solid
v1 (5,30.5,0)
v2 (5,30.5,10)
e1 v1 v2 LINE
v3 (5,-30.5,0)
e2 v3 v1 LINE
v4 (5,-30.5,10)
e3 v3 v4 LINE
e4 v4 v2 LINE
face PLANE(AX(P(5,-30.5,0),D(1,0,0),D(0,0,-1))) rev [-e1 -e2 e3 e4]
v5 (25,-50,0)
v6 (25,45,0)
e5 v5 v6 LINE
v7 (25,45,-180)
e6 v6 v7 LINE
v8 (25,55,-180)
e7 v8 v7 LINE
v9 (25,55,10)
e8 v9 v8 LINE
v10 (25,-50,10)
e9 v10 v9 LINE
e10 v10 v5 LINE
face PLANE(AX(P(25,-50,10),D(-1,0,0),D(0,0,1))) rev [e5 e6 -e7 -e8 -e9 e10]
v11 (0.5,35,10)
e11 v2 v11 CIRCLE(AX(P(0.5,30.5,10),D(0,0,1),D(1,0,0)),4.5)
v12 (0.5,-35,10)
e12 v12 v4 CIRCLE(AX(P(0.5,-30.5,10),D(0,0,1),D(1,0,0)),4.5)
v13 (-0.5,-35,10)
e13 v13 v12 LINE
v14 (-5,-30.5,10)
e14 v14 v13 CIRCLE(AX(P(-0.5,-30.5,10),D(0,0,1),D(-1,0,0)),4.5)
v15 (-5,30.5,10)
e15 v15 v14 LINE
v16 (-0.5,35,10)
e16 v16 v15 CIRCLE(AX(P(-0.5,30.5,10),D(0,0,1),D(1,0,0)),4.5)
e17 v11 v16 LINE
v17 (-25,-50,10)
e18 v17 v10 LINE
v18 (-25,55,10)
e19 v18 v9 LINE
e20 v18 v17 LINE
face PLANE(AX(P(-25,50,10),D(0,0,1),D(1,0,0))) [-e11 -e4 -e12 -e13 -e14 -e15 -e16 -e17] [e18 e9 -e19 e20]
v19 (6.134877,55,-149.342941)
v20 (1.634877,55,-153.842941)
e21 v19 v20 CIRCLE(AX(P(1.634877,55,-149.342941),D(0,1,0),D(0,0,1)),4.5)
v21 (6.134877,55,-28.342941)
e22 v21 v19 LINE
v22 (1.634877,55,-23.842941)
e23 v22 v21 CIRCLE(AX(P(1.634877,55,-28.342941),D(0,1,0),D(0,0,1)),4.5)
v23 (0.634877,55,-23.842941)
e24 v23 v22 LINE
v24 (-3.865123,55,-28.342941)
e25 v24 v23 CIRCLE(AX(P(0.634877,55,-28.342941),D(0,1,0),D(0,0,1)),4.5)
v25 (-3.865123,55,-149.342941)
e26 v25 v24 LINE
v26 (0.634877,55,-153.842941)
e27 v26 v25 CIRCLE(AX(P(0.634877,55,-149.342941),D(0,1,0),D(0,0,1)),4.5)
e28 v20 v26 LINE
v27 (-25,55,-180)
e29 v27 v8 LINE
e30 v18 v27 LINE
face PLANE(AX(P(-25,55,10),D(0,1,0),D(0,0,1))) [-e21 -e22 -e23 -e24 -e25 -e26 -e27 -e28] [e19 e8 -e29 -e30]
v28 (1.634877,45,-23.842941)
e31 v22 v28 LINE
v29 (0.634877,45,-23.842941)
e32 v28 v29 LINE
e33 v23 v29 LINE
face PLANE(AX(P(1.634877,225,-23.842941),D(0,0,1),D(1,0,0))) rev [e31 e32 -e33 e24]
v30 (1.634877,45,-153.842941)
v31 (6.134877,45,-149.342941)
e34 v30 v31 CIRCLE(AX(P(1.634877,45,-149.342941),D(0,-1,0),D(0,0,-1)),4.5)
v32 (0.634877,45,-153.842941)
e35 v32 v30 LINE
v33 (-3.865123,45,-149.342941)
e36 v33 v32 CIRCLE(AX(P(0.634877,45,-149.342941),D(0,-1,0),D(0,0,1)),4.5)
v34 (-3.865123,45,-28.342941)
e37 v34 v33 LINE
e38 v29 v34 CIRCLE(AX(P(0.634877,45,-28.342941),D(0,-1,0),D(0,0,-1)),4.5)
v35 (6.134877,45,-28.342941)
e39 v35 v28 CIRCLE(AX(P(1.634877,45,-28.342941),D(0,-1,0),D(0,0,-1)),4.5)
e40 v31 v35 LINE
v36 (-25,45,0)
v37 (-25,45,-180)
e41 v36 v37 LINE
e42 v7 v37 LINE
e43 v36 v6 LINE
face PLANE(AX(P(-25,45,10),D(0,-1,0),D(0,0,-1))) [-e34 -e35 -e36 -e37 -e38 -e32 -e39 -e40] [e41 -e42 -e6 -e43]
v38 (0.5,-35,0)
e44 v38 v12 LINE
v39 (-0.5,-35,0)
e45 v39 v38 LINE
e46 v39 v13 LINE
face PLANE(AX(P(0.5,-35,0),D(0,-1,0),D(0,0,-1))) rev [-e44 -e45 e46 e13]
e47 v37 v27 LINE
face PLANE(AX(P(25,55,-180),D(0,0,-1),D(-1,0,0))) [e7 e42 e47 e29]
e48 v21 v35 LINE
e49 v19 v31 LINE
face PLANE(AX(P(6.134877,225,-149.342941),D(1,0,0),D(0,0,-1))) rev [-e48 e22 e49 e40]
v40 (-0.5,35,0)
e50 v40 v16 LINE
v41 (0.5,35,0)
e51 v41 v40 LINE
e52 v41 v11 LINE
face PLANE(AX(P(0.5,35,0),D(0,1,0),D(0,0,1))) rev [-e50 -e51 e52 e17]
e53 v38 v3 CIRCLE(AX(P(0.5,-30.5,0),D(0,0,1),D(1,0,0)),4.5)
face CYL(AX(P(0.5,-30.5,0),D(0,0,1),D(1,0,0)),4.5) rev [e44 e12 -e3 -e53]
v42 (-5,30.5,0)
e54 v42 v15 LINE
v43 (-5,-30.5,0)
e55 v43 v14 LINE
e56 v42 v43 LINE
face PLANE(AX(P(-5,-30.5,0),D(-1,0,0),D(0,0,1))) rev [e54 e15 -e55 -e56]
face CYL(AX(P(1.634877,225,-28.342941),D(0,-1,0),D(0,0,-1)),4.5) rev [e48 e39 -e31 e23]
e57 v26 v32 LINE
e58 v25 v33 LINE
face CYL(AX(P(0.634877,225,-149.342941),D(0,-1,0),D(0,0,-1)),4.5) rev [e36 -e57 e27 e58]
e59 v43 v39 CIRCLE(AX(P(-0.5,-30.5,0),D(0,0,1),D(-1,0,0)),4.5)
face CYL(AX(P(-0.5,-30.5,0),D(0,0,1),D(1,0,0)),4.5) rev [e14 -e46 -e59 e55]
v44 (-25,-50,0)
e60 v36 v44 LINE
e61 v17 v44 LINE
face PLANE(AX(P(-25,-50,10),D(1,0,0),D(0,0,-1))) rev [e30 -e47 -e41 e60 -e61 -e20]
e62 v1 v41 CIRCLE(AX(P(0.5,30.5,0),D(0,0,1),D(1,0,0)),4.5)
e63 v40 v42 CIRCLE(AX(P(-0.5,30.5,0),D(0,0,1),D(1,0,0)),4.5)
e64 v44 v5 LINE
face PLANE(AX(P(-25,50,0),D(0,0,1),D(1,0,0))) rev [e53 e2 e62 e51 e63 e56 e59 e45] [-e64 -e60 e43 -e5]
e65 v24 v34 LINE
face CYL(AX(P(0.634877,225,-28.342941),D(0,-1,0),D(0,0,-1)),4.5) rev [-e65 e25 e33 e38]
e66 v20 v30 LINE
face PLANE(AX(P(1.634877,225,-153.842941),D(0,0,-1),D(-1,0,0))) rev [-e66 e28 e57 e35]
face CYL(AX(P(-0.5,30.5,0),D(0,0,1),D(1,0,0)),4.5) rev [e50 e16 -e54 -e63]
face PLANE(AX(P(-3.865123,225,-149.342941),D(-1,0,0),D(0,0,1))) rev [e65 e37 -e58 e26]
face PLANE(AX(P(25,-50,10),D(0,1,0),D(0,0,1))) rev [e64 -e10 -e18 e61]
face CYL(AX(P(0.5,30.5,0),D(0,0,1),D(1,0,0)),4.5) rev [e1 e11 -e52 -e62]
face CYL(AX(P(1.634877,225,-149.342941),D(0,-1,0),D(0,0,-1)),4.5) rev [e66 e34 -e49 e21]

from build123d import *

# Parameters (mm, degrees)
SKETCH1_W                = 50
SKETCH1_H                = 100
BOSS_EXTRUDE1_DEPTH      = 10
CUT_EXTRUDE1_DEPTH       = 10
BOSS_EXTRUDE2_DEPTH      = 180
BOSS_EXTRUDE2_DEPTH_BACK = 10
SKETCH3_W                = 50
SKETCH3_H                = 10
CUT_EXTRUDE2_DEPTH       = 180


with BuildPart() as part:
    # Sketch1 → Boss-Extrude1 (new body)
    with BuildSketch(Plane.XY):
        Rectangle(SKETCH1_W, SKETCH1_H)
    extrude(amount=BOSS_EXTRUDE1_DEPTH)

    # Sketch2 → Cut-Extrude1 (cut)
    with BuildSketch(Plane.XY.offset(10)):
        with BuildLine():
            Line((0.5, -35), (-0.5, -35))
            ThreePointArc((-0.5, -35), (-3.681980515, -33.681980515), (-5, -30.5))
            Line((-5, -30.5), (-5, 30.5))
            ThreePointArc((-5, 30.5), (-3.681980515, 33.681980515), (-0.5, 35))
            Line((-0.5, 35), (0.5, 35))
            ThreePointArc((0.5, 35), (3.681980515, 33.681980515), (5, 30.5))
            Line((5, 30.5), (5, -30.5))
            ThreePointArc((5, -30.5), (3.681980515, -33.681980515), (0.5, -35))
        make_face()
    extrude(amount=-CUT_EXTRUDE1_DEPTH, mode=Mode.SUBTRACT)

    # Sketch3 → Boss-Extrude2 (add, two sides: drawn at the far end of the back side and taken through both)
    with BuildSketch(Plane(origin=(0, 0, 0), x_dir=(-1, 0, 0), z_dir=(0, 0, -1)).offset(-BOSS_EXTRUDE2_DEPTH_BACK)):
        with Locations((0, 50)):
            Rectangle(SKETCH3_W, SKETCH3_H)
    extrude(amount=BOSS_EXTRUDE2_DEPTH + BOSS_EXTRUDE2_DEPTH_BACK)

    # Sketch4 → Cut-Extrude2 (cut)
    with BuildSketch(Plane.XZ.offset(-45)):
        with BuildLine():
            Line((1.63487738, -153.842941115), (0.63487738, -153.842941115))
            ThreePointArc((0.63487738, -153.842941115), (-2.547103135, -152.52492163), (-3.86512262, -149.342941115))
            Line((-3.86512262, -149.342941115), (-3.86512262, -28.342941115))
            ThreePointArc((-3.86512262, -28.342941115), (-2.547103135, -25.160960599), (0.63487738, -23.842941115))
            Line((0.63487738, -23.842941115), (1.63487738, -23.842941115))
            ThreePointArc((1.63487738, -23.842941115), (4.816857896, -25.160960599), (6.13487738, -28.342941115))
            Line((6.13487738, -28.342941115), (6.13487738, -149.342941115))
            ThreePointArc((6.13487738, -149.342941115), (4.816857896, -152.52492163), (1.63487738, -153.842941115))
        make_face()
    extrude(amount=-CUT_EXTRUDE2_DEPTH, mode=Mode.SUBTRACT)


solid = part.part
